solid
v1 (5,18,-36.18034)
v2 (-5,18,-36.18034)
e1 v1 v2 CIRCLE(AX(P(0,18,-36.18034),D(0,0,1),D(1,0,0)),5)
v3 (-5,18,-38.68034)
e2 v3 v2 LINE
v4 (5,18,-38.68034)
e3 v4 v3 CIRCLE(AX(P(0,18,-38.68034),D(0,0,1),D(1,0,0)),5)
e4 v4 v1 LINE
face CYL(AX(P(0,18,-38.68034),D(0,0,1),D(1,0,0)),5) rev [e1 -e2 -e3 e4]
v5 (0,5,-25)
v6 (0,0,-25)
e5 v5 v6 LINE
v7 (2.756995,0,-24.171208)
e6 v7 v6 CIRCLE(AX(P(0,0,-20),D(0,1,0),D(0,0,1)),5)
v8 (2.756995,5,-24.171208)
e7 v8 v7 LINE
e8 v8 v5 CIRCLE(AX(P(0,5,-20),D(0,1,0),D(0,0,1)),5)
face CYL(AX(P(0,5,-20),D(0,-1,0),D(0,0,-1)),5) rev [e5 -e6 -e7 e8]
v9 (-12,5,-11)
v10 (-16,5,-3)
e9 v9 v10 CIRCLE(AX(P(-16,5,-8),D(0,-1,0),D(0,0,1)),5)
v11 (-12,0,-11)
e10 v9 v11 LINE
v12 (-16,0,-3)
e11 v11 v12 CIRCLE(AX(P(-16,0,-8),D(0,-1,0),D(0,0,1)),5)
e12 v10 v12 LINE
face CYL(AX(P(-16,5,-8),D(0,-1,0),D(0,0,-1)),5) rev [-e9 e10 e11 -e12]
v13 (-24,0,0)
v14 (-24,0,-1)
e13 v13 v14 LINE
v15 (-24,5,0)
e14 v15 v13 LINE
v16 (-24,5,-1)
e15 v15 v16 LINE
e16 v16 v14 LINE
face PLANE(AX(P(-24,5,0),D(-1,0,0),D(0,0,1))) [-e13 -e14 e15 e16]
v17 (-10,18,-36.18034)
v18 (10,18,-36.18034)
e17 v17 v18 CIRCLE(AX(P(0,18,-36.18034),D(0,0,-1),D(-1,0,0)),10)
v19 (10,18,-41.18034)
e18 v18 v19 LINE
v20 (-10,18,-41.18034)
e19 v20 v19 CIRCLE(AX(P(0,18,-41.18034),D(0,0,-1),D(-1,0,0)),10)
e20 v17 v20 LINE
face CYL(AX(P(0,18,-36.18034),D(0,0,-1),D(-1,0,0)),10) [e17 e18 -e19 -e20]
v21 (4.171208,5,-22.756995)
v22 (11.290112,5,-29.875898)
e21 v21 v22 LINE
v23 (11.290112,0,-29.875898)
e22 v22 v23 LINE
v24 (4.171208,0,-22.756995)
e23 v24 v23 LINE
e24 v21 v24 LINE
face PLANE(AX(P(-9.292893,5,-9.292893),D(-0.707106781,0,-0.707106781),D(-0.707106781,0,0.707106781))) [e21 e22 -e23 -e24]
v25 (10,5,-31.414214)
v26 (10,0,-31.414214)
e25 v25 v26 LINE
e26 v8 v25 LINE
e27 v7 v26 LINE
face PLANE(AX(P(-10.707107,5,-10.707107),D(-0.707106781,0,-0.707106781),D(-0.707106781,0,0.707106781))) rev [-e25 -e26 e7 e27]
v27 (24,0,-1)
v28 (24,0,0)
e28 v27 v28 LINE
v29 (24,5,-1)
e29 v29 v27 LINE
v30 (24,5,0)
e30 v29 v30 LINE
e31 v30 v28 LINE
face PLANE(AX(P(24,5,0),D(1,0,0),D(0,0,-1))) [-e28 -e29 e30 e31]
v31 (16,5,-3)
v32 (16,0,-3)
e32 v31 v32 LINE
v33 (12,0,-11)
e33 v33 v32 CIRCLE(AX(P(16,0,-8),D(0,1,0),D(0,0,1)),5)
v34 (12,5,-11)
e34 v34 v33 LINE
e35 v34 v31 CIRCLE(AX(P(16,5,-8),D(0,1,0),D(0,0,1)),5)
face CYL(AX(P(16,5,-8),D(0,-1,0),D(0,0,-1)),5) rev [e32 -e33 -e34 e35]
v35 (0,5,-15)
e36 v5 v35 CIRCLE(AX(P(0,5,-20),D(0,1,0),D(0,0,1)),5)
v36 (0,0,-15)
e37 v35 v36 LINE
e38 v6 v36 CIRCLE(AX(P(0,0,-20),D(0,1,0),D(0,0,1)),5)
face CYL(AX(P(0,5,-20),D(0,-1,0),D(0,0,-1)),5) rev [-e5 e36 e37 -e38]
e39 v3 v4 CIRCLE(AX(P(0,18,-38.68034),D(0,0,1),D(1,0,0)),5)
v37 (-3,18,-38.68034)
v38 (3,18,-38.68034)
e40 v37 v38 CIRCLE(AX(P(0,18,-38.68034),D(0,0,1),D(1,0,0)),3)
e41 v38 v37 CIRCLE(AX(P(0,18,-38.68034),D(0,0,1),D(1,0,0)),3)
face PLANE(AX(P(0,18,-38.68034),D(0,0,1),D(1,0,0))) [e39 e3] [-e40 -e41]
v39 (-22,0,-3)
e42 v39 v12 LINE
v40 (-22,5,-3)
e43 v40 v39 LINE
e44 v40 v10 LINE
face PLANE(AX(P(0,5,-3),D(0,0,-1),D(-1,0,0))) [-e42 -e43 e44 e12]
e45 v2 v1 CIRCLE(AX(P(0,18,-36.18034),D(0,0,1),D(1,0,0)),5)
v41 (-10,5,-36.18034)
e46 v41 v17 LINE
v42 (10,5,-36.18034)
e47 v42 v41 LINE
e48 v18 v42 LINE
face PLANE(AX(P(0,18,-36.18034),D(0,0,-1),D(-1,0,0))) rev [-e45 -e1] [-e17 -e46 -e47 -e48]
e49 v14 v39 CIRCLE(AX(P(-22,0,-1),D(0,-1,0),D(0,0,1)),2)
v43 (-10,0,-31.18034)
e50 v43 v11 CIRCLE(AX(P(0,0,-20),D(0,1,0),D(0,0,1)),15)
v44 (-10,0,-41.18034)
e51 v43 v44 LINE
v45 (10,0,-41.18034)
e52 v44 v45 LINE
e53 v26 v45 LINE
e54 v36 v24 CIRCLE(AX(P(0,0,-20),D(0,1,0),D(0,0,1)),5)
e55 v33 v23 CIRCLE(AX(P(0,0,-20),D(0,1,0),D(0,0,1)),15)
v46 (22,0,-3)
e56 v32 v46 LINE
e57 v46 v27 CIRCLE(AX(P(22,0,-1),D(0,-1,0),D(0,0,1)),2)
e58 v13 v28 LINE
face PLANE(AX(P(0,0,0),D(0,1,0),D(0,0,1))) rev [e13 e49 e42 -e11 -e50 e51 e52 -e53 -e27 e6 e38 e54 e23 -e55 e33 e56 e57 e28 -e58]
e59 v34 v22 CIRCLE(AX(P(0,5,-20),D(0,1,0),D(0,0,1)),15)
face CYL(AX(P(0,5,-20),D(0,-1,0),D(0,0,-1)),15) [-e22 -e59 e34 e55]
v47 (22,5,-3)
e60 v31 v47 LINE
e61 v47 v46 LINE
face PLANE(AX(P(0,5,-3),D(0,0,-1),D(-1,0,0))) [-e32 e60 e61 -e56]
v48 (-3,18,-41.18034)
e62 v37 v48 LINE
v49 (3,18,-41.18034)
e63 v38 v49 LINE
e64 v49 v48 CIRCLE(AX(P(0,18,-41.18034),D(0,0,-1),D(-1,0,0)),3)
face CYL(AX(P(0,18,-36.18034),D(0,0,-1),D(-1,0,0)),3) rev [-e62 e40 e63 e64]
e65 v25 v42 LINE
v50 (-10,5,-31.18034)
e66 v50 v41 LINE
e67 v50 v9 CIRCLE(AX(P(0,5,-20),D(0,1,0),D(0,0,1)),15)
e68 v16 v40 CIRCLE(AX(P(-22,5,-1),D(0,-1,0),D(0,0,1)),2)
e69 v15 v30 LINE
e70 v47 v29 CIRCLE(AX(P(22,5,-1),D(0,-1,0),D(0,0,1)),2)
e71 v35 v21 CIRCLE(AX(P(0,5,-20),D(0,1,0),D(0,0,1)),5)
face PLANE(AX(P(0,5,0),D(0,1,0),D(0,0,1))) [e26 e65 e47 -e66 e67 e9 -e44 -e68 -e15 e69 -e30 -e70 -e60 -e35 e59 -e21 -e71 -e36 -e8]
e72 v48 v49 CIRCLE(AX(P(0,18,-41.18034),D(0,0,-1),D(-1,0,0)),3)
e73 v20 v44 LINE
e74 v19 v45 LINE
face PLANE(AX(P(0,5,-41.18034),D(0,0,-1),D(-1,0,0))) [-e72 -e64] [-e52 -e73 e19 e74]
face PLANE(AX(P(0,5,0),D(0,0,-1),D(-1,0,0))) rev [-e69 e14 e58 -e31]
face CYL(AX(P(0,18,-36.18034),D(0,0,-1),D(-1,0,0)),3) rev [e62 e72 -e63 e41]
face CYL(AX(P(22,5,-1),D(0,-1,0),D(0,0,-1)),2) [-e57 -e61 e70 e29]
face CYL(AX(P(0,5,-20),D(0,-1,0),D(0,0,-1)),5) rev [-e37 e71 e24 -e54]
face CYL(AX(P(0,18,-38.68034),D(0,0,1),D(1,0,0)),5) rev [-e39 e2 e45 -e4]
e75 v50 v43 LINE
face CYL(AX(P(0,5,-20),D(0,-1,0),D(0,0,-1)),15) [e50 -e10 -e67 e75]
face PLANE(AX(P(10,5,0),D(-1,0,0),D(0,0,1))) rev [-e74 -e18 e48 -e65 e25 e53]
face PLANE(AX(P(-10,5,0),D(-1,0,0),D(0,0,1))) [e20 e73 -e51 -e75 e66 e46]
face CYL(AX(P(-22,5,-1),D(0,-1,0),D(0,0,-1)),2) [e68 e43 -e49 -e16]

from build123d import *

# Parameters (mm, degrees)
BASE_PLATE_5MM_DEPTH           = 5
UPRIGHT_LUG_PROFILE_SKETCH_R   = 3
UPRIGHT_LUG_DEPTH              = 5
PIVOT_START                    = -2.5
PIVOT_COUNTERBORE_SKETCH_R     = 5
PIVOT_COUNTERBORE_SKETCH_R_2   = 3
PIVOT_COUNTERBORE_10X2_5_DEPTH = 2.5


with BuildPart() as part:
    # Base Plate Profile Sketch → Base Plate 5mm (new body)
    with BuildSketch(Plane(origin=(0, 0, 0), x_dir=(1, 0, 0), z_dir=(0, 1, 0))):
        with BuildLine():
            Line((-24, 1), (-24, 0))
            Line((-24, 0), (24, 0))
            Line((24, 0), (24, 1))
            ThreePointArc((24, 1), (23.414213562, 2.414213562), (22, 3))
            Line((22, 3), (16, 3))
            ThreePointArc((16, 3), (11.527864045, 5.763932023), (12, 11))
            ThreePointArc((12, 11), (14.989403432, 20.563724014), (11.290112025, 29.875898463))
            Line((11.290112025, 29.875898463), (4.171208396, 22.756994834))
            ThreePointArc((4.171208396, 22.756994834), (-3.535533906, 16.464466094), (2.756994834, 24.171208396))
            Line((2.756994834, 24.171208396), (10, 31.414213562))
            Line((10, 31.414213562), (10, 35))
            Line((10, 35), (10, 41.180339887))
            Line((10, 41.180339887), (-10, 41.180339887))
            Line((-10, 41.180339887), (-10, 35))
            Line((-10, 35), (-10, 31.180339887))
            ThreePointArc((-10, 31.180339887), (-14.92687273, 21.479348), (-12, 11))
            ThreePointArc((-12, 11), (-11.527864045, 5.763932023), (-16, 3))
            Line((-16, 3), (-22, 3))
            ThreePointArc((-22, 3), (-23.414213562, 2.414213562), (-24, 1))
        make_face()
    extrude(amount=BASE_PLATE_5MM_DEPTH)

    # Upright Lug Profile Sketch → Upright Lug (add)
    with BuildSketch(Plane(origin=(0, 0, -41.180339887), x_dir=(-1, 0, 0), z_dir=(0, 0, -1))):
        with BuildLine():
            Line((-10, 18), (-10, 0))
            Line((-10, 0), (10, 0))
            Line((10, 0), (10, 18))
            ThreePointArc((10, 18), (0, 28), (-10, 18))
        make_face()
        with Locations((0, 18)):
            Circle(UPRIGHT_LUG_PROFILE_SKETCH_R, mode=Mode.SUBTRACT)
    extrude(amount=-UPRIGHT_LUG_DEPTH)

    # Pivot Counterbore Sketch → Pivot Counterbore Ø10x2.5 (cut)
    with BuildSketch(Plane.XY.offset(-36.180339887).offset(PIVOT_START)):
        with Locations((0, 18)):
            Circle(PIVOT_COUNTERBORE_SKETCH_R)
        with Locations(Location((0, 18, 0), (0, 0, 180))):
            Circle(PIVOT_COUNTERBORE_SKETCH_R_2, mode=Mode.SUBTRACT)
    extrude(amount=PIVOT_COUNTERBORE_10X2_5_DEPTH, mode=Mode.SUBTRACT)


solid = part.part
